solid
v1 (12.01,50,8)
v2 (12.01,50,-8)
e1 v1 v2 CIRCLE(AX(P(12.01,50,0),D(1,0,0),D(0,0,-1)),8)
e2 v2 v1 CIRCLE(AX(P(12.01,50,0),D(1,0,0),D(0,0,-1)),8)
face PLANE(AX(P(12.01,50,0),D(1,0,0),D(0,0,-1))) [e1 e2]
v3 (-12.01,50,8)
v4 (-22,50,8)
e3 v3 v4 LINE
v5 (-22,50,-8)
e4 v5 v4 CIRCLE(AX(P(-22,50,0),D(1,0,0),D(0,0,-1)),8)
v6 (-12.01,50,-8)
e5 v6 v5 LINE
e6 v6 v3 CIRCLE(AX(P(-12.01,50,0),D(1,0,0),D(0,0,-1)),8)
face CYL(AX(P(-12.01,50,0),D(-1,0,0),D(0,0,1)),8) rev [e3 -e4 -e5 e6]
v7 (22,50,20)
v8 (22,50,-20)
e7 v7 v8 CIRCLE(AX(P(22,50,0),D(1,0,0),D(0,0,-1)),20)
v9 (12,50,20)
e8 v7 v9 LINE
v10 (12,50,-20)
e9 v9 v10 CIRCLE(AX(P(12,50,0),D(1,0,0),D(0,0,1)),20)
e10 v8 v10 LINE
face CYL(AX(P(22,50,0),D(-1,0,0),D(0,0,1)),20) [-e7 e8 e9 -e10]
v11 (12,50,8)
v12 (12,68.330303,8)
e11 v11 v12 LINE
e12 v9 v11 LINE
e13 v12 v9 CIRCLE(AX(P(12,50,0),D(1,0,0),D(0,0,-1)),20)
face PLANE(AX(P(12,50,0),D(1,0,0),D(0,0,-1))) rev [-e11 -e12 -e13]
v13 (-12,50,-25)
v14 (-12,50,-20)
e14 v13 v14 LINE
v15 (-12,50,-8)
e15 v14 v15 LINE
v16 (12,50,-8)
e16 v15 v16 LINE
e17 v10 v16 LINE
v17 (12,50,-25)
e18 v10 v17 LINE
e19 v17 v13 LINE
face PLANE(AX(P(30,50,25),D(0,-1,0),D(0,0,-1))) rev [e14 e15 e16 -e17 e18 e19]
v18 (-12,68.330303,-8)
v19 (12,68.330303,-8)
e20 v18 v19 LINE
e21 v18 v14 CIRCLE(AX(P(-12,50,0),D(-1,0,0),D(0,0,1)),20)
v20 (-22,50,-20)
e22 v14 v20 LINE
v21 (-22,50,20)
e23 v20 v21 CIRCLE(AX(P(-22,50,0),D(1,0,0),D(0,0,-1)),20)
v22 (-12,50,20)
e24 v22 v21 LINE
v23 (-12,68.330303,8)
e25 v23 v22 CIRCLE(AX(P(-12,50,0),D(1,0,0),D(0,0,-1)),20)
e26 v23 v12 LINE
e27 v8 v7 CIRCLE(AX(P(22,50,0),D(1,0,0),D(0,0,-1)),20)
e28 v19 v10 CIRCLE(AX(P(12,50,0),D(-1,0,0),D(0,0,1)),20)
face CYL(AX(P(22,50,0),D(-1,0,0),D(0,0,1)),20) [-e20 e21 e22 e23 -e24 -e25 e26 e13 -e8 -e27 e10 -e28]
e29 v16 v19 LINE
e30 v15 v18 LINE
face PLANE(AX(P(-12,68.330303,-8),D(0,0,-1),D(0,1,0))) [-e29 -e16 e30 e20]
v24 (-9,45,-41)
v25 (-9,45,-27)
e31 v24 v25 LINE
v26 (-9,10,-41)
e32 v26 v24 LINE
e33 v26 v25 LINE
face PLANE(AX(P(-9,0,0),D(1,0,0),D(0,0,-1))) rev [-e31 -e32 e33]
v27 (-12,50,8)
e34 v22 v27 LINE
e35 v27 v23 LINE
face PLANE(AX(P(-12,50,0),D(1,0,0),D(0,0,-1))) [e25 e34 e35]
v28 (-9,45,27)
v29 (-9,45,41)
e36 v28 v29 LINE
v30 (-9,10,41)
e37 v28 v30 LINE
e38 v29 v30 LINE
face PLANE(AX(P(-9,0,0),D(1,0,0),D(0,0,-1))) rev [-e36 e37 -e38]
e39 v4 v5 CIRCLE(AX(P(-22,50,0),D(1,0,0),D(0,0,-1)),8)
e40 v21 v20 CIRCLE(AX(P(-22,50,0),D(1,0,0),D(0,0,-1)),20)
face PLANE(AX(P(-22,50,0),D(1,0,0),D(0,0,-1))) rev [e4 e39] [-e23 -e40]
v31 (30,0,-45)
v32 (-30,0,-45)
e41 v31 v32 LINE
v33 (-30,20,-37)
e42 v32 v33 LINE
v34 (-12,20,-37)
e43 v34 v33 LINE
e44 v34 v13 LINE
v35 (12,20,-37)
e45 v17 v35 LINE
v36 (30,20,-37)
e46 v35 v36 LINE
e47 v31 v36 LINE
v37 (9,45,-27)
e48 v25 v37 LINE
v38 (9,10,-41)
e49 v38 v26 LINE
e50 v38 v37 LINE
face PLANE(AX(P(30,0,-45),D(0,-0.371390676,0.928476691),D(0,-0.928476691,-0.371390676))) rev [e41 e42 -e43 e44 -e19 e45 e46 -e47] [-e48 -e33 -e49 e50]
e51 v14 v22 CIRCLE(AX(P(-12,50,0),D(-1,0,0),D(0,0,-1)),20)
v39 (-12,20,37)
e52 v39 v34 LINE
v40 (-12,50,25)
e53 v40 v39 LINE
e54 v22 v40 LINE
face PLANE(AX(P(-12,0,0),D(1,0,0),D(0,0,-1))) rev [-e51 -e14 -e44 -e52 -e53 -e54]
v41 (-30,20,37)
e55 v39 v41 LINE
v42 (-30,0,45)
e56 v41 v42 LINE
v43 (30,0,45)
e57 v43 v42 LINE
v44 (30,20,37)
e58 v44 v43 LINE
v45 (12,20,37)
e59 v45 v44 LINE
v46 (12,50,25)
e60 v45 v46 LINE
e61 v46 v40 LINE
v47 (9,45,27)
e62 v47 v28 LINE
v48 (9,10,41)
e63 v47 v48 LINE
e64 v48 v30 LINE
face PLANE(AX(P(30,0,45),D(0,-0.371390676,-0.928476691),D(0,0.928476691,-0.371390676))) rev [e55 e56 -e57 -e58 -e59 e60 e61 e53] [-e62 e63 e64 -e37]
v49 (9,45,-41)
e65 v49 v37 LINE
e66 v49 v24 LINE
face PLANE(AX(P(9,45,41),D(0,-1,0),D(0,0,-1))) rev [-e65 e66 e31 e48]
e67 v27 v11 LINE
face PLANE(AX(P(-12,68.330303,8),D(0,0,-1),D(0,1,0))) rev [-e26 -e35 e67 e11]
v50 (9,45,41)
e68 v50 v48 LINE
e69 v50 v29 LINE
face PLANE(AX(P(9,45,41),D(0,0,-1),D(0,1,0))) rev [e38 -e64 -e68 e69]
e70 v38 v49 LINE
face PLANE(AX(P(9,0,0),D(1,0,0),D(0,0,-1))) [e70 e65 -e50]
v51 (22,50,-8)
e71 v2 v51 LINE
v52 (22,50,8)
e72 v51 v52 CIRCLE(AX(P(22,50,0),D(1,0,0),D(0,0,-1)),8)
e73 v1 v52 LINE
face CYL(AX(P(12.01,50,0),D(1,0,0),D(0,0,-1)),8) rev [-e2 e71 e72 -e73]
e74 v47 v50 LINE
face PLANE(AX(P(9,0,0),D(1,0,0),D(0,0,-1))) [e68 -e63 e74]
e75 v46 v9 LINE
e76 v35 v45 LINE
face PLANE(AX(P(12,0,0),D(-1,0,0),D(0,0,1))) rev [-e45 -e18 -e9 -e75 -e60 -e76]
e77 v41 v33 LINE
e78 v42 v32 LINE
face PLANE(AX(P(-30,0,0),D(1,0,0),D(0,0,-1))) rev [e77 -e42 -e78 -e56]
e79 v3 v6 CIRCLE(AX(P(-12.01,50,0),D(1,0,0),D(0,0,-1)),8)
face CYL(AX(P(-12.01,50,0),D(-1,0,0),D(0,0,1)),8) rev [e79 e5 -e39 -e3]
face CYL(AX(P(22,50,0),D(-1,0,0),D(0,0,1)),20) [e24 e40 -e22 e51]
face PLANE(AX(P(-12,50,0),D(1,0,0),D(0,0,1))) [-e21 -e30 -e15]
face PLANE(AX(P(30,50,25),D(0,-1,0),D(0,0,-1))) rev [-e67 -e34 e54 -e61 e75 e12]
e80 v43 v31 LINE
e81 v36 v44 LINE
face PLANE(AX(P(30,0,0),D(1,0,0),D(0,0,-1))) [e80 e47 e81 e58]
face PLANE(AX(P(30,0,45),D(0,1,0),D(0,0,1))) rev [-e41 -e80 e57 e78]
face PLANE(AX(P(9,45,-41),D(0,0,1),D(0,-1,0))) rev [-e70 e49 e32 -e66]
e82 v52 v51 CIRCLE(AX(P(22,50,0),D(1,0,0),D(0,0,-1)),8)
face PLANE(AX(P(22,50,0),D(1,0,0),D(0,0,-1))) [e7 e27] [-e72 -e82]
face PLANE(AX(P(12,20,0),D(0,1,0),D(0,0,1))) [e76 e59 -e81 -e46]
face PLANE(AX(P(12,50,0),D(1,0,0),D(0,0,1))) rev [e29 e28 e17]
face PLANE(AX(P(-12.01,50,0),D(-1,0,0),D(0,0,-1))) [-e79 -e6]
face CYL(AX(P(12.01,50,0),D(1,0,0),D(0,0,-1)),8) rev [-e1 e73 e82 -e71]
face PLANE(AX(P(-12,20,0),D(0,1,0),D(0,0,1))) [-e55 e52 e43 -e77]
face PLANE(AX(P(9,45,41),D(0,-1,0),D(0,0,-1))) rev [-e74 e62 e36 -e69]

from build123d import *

# Parameters (mm, degrees)
BASE_BODY_DEPTH         = 30
SIDE_START              = -30
SIDE_POCKET_CUT_1_DEPTH = 18
SIDE_START_2            = 30
SIDE_POCKET_CUT_2_DEPTH = 18
SIDE_BLOCK_SKETCH_W     = 82
SIDE_BLOCK_SKETCH_H     = 35
SIDE_BLOCK_45X35_DEPTH  = 9
PIVOT_CYLINDER_SKETCH_R = 20
PIVOT_CYLINDER_40_DEPTH = 22
CYLINDER_SLOT_CUT_DEPTH = 12
PIVOT_BORE_SKETCH_R     = 8
PIVOT_BORE_16_DEPTH     = 9.99


with BuildPart() as part:
    # Base Profile Sketch → Base Body (new, symmetric)
    with BuildSketch(Plane(origin=(0, 0, 0), x_dir=(0, 0, -1), z_dir=(1, 0, 0))):
        Polygon((-45, 0), (45, 0), (25, 50), (0, 50), (-25, 50), align=None)
    extrude(amount=BASE_BODY_DEPTH, both=True)

    # Side Pocket Sketch → Side Pocket Cut 1 (cut)
    with BuildSketch(Plane(origin=(0, 0, 0), x_dir=(0, 0, -1), z_dir=(1, 0, 0)).offset(SIDE_START)):
        Polygon((-37, 20), (37, 20), (25, 50), (-25, 50), align=None)
    extrude(amount=SIDE_POCKET_CUT_1_DEPTH, mode=Mode.SUBTRACT)

    # Sketch5_2 → Side Pocket Cut 2 (cut)
    with BuildSketch(Plane(origin=(0, 0, 0), x_dir=(0, 0, -1), z_dir=(1, 0, 0)).offset(SIDE_START_2)):
        Polygon((-37, 20), (37, 20), (25, 50), (-25, 50), align=None)
    extrude(amount=-SIDE_POCKET_CUT_2_DEPTH, mode=Mode.SUBTRACT)

    # Side Block Sketch → Side Block 45x35 (add, symmetric)
    with BuildSketch(Plane(origin=(0, 0, 0), x_dir=(0, 0, -1), z_dir=(1, 0, 0))):
        with Locations((0, 27.5)):
            Rectangle(SIDE_BLOCK_SKETCH_W, SIDE_BLOCK_SKETCH_H)
    extrude(amount=SIDE_BLOCK_45X35_DEPTH, both=True)

    # Pivot Cylinder Sketch → Pivot Cylinder _40 (add, symmetric)
    with BuildSketch(Plane(origin=(0, 0, 0), x_dir=(0, 0, -1), z_dir=(1, 0, 0))):
        with Locations((0, 50)):
            Circle(PIVOT_CYLINDER_SKETCH_R)
    extrude(amount=PIVOT_CYLINDER_40_DEPTH, both=True)

    # Cylinder Slot Sketch → Cylinder Slot Cut (cut, symmetric)
    with BuildSketch(Plane(origin=(0, 0, 0), x_dir=(0, 0, -1), z_dir=(1, 0, 0))):
        with BuildLine():
            Line((-8, 68.33030278), (-8, 50))
            Line((-8, 50), (-20, 50))
            ThreePointArc((-20, 50), (-16.733200531, 60.95445115), (-8, 68.33030278))
        make_face()
    cylinder_slot_cut = extrude(amount=CYLINDER_SLOT_CUT_DEPTH, both=True, mode=Mode.SUBTRACT)

    # Cylinder Slot Mirror: Cylinder Slot Cut across plane
    add(cylinder_slot_cut.mirror(Plane.XY), mode=Mode.SUBTRACT)

    # Pivot Bore Sketch → Pivot Bore _16 (cut)
    with BuildSketch(Plane(origin=(22, 0, 0), x_dir=(0, 0, -1), z_dir=(1, 0, 0))):
        with Locations((0, 50)):
            Circle(PIVOT_BORE_SKETCH_R)
    pivot_bore_16 = extrude(amount=-PIVOT_BORE_16_DEPTH, mode=Mode.SUBTRACT)

    # Pivot Bore Mirror: Pivot Bore _16 across plane
    add(pivot_bore_16.mirror(Plane(origin=(0, 0, 0), x_dir=(0, 0, 1), z_dir=(1, 0, 0))), mode=Mode.SUBTRACT)


solid = part.part
